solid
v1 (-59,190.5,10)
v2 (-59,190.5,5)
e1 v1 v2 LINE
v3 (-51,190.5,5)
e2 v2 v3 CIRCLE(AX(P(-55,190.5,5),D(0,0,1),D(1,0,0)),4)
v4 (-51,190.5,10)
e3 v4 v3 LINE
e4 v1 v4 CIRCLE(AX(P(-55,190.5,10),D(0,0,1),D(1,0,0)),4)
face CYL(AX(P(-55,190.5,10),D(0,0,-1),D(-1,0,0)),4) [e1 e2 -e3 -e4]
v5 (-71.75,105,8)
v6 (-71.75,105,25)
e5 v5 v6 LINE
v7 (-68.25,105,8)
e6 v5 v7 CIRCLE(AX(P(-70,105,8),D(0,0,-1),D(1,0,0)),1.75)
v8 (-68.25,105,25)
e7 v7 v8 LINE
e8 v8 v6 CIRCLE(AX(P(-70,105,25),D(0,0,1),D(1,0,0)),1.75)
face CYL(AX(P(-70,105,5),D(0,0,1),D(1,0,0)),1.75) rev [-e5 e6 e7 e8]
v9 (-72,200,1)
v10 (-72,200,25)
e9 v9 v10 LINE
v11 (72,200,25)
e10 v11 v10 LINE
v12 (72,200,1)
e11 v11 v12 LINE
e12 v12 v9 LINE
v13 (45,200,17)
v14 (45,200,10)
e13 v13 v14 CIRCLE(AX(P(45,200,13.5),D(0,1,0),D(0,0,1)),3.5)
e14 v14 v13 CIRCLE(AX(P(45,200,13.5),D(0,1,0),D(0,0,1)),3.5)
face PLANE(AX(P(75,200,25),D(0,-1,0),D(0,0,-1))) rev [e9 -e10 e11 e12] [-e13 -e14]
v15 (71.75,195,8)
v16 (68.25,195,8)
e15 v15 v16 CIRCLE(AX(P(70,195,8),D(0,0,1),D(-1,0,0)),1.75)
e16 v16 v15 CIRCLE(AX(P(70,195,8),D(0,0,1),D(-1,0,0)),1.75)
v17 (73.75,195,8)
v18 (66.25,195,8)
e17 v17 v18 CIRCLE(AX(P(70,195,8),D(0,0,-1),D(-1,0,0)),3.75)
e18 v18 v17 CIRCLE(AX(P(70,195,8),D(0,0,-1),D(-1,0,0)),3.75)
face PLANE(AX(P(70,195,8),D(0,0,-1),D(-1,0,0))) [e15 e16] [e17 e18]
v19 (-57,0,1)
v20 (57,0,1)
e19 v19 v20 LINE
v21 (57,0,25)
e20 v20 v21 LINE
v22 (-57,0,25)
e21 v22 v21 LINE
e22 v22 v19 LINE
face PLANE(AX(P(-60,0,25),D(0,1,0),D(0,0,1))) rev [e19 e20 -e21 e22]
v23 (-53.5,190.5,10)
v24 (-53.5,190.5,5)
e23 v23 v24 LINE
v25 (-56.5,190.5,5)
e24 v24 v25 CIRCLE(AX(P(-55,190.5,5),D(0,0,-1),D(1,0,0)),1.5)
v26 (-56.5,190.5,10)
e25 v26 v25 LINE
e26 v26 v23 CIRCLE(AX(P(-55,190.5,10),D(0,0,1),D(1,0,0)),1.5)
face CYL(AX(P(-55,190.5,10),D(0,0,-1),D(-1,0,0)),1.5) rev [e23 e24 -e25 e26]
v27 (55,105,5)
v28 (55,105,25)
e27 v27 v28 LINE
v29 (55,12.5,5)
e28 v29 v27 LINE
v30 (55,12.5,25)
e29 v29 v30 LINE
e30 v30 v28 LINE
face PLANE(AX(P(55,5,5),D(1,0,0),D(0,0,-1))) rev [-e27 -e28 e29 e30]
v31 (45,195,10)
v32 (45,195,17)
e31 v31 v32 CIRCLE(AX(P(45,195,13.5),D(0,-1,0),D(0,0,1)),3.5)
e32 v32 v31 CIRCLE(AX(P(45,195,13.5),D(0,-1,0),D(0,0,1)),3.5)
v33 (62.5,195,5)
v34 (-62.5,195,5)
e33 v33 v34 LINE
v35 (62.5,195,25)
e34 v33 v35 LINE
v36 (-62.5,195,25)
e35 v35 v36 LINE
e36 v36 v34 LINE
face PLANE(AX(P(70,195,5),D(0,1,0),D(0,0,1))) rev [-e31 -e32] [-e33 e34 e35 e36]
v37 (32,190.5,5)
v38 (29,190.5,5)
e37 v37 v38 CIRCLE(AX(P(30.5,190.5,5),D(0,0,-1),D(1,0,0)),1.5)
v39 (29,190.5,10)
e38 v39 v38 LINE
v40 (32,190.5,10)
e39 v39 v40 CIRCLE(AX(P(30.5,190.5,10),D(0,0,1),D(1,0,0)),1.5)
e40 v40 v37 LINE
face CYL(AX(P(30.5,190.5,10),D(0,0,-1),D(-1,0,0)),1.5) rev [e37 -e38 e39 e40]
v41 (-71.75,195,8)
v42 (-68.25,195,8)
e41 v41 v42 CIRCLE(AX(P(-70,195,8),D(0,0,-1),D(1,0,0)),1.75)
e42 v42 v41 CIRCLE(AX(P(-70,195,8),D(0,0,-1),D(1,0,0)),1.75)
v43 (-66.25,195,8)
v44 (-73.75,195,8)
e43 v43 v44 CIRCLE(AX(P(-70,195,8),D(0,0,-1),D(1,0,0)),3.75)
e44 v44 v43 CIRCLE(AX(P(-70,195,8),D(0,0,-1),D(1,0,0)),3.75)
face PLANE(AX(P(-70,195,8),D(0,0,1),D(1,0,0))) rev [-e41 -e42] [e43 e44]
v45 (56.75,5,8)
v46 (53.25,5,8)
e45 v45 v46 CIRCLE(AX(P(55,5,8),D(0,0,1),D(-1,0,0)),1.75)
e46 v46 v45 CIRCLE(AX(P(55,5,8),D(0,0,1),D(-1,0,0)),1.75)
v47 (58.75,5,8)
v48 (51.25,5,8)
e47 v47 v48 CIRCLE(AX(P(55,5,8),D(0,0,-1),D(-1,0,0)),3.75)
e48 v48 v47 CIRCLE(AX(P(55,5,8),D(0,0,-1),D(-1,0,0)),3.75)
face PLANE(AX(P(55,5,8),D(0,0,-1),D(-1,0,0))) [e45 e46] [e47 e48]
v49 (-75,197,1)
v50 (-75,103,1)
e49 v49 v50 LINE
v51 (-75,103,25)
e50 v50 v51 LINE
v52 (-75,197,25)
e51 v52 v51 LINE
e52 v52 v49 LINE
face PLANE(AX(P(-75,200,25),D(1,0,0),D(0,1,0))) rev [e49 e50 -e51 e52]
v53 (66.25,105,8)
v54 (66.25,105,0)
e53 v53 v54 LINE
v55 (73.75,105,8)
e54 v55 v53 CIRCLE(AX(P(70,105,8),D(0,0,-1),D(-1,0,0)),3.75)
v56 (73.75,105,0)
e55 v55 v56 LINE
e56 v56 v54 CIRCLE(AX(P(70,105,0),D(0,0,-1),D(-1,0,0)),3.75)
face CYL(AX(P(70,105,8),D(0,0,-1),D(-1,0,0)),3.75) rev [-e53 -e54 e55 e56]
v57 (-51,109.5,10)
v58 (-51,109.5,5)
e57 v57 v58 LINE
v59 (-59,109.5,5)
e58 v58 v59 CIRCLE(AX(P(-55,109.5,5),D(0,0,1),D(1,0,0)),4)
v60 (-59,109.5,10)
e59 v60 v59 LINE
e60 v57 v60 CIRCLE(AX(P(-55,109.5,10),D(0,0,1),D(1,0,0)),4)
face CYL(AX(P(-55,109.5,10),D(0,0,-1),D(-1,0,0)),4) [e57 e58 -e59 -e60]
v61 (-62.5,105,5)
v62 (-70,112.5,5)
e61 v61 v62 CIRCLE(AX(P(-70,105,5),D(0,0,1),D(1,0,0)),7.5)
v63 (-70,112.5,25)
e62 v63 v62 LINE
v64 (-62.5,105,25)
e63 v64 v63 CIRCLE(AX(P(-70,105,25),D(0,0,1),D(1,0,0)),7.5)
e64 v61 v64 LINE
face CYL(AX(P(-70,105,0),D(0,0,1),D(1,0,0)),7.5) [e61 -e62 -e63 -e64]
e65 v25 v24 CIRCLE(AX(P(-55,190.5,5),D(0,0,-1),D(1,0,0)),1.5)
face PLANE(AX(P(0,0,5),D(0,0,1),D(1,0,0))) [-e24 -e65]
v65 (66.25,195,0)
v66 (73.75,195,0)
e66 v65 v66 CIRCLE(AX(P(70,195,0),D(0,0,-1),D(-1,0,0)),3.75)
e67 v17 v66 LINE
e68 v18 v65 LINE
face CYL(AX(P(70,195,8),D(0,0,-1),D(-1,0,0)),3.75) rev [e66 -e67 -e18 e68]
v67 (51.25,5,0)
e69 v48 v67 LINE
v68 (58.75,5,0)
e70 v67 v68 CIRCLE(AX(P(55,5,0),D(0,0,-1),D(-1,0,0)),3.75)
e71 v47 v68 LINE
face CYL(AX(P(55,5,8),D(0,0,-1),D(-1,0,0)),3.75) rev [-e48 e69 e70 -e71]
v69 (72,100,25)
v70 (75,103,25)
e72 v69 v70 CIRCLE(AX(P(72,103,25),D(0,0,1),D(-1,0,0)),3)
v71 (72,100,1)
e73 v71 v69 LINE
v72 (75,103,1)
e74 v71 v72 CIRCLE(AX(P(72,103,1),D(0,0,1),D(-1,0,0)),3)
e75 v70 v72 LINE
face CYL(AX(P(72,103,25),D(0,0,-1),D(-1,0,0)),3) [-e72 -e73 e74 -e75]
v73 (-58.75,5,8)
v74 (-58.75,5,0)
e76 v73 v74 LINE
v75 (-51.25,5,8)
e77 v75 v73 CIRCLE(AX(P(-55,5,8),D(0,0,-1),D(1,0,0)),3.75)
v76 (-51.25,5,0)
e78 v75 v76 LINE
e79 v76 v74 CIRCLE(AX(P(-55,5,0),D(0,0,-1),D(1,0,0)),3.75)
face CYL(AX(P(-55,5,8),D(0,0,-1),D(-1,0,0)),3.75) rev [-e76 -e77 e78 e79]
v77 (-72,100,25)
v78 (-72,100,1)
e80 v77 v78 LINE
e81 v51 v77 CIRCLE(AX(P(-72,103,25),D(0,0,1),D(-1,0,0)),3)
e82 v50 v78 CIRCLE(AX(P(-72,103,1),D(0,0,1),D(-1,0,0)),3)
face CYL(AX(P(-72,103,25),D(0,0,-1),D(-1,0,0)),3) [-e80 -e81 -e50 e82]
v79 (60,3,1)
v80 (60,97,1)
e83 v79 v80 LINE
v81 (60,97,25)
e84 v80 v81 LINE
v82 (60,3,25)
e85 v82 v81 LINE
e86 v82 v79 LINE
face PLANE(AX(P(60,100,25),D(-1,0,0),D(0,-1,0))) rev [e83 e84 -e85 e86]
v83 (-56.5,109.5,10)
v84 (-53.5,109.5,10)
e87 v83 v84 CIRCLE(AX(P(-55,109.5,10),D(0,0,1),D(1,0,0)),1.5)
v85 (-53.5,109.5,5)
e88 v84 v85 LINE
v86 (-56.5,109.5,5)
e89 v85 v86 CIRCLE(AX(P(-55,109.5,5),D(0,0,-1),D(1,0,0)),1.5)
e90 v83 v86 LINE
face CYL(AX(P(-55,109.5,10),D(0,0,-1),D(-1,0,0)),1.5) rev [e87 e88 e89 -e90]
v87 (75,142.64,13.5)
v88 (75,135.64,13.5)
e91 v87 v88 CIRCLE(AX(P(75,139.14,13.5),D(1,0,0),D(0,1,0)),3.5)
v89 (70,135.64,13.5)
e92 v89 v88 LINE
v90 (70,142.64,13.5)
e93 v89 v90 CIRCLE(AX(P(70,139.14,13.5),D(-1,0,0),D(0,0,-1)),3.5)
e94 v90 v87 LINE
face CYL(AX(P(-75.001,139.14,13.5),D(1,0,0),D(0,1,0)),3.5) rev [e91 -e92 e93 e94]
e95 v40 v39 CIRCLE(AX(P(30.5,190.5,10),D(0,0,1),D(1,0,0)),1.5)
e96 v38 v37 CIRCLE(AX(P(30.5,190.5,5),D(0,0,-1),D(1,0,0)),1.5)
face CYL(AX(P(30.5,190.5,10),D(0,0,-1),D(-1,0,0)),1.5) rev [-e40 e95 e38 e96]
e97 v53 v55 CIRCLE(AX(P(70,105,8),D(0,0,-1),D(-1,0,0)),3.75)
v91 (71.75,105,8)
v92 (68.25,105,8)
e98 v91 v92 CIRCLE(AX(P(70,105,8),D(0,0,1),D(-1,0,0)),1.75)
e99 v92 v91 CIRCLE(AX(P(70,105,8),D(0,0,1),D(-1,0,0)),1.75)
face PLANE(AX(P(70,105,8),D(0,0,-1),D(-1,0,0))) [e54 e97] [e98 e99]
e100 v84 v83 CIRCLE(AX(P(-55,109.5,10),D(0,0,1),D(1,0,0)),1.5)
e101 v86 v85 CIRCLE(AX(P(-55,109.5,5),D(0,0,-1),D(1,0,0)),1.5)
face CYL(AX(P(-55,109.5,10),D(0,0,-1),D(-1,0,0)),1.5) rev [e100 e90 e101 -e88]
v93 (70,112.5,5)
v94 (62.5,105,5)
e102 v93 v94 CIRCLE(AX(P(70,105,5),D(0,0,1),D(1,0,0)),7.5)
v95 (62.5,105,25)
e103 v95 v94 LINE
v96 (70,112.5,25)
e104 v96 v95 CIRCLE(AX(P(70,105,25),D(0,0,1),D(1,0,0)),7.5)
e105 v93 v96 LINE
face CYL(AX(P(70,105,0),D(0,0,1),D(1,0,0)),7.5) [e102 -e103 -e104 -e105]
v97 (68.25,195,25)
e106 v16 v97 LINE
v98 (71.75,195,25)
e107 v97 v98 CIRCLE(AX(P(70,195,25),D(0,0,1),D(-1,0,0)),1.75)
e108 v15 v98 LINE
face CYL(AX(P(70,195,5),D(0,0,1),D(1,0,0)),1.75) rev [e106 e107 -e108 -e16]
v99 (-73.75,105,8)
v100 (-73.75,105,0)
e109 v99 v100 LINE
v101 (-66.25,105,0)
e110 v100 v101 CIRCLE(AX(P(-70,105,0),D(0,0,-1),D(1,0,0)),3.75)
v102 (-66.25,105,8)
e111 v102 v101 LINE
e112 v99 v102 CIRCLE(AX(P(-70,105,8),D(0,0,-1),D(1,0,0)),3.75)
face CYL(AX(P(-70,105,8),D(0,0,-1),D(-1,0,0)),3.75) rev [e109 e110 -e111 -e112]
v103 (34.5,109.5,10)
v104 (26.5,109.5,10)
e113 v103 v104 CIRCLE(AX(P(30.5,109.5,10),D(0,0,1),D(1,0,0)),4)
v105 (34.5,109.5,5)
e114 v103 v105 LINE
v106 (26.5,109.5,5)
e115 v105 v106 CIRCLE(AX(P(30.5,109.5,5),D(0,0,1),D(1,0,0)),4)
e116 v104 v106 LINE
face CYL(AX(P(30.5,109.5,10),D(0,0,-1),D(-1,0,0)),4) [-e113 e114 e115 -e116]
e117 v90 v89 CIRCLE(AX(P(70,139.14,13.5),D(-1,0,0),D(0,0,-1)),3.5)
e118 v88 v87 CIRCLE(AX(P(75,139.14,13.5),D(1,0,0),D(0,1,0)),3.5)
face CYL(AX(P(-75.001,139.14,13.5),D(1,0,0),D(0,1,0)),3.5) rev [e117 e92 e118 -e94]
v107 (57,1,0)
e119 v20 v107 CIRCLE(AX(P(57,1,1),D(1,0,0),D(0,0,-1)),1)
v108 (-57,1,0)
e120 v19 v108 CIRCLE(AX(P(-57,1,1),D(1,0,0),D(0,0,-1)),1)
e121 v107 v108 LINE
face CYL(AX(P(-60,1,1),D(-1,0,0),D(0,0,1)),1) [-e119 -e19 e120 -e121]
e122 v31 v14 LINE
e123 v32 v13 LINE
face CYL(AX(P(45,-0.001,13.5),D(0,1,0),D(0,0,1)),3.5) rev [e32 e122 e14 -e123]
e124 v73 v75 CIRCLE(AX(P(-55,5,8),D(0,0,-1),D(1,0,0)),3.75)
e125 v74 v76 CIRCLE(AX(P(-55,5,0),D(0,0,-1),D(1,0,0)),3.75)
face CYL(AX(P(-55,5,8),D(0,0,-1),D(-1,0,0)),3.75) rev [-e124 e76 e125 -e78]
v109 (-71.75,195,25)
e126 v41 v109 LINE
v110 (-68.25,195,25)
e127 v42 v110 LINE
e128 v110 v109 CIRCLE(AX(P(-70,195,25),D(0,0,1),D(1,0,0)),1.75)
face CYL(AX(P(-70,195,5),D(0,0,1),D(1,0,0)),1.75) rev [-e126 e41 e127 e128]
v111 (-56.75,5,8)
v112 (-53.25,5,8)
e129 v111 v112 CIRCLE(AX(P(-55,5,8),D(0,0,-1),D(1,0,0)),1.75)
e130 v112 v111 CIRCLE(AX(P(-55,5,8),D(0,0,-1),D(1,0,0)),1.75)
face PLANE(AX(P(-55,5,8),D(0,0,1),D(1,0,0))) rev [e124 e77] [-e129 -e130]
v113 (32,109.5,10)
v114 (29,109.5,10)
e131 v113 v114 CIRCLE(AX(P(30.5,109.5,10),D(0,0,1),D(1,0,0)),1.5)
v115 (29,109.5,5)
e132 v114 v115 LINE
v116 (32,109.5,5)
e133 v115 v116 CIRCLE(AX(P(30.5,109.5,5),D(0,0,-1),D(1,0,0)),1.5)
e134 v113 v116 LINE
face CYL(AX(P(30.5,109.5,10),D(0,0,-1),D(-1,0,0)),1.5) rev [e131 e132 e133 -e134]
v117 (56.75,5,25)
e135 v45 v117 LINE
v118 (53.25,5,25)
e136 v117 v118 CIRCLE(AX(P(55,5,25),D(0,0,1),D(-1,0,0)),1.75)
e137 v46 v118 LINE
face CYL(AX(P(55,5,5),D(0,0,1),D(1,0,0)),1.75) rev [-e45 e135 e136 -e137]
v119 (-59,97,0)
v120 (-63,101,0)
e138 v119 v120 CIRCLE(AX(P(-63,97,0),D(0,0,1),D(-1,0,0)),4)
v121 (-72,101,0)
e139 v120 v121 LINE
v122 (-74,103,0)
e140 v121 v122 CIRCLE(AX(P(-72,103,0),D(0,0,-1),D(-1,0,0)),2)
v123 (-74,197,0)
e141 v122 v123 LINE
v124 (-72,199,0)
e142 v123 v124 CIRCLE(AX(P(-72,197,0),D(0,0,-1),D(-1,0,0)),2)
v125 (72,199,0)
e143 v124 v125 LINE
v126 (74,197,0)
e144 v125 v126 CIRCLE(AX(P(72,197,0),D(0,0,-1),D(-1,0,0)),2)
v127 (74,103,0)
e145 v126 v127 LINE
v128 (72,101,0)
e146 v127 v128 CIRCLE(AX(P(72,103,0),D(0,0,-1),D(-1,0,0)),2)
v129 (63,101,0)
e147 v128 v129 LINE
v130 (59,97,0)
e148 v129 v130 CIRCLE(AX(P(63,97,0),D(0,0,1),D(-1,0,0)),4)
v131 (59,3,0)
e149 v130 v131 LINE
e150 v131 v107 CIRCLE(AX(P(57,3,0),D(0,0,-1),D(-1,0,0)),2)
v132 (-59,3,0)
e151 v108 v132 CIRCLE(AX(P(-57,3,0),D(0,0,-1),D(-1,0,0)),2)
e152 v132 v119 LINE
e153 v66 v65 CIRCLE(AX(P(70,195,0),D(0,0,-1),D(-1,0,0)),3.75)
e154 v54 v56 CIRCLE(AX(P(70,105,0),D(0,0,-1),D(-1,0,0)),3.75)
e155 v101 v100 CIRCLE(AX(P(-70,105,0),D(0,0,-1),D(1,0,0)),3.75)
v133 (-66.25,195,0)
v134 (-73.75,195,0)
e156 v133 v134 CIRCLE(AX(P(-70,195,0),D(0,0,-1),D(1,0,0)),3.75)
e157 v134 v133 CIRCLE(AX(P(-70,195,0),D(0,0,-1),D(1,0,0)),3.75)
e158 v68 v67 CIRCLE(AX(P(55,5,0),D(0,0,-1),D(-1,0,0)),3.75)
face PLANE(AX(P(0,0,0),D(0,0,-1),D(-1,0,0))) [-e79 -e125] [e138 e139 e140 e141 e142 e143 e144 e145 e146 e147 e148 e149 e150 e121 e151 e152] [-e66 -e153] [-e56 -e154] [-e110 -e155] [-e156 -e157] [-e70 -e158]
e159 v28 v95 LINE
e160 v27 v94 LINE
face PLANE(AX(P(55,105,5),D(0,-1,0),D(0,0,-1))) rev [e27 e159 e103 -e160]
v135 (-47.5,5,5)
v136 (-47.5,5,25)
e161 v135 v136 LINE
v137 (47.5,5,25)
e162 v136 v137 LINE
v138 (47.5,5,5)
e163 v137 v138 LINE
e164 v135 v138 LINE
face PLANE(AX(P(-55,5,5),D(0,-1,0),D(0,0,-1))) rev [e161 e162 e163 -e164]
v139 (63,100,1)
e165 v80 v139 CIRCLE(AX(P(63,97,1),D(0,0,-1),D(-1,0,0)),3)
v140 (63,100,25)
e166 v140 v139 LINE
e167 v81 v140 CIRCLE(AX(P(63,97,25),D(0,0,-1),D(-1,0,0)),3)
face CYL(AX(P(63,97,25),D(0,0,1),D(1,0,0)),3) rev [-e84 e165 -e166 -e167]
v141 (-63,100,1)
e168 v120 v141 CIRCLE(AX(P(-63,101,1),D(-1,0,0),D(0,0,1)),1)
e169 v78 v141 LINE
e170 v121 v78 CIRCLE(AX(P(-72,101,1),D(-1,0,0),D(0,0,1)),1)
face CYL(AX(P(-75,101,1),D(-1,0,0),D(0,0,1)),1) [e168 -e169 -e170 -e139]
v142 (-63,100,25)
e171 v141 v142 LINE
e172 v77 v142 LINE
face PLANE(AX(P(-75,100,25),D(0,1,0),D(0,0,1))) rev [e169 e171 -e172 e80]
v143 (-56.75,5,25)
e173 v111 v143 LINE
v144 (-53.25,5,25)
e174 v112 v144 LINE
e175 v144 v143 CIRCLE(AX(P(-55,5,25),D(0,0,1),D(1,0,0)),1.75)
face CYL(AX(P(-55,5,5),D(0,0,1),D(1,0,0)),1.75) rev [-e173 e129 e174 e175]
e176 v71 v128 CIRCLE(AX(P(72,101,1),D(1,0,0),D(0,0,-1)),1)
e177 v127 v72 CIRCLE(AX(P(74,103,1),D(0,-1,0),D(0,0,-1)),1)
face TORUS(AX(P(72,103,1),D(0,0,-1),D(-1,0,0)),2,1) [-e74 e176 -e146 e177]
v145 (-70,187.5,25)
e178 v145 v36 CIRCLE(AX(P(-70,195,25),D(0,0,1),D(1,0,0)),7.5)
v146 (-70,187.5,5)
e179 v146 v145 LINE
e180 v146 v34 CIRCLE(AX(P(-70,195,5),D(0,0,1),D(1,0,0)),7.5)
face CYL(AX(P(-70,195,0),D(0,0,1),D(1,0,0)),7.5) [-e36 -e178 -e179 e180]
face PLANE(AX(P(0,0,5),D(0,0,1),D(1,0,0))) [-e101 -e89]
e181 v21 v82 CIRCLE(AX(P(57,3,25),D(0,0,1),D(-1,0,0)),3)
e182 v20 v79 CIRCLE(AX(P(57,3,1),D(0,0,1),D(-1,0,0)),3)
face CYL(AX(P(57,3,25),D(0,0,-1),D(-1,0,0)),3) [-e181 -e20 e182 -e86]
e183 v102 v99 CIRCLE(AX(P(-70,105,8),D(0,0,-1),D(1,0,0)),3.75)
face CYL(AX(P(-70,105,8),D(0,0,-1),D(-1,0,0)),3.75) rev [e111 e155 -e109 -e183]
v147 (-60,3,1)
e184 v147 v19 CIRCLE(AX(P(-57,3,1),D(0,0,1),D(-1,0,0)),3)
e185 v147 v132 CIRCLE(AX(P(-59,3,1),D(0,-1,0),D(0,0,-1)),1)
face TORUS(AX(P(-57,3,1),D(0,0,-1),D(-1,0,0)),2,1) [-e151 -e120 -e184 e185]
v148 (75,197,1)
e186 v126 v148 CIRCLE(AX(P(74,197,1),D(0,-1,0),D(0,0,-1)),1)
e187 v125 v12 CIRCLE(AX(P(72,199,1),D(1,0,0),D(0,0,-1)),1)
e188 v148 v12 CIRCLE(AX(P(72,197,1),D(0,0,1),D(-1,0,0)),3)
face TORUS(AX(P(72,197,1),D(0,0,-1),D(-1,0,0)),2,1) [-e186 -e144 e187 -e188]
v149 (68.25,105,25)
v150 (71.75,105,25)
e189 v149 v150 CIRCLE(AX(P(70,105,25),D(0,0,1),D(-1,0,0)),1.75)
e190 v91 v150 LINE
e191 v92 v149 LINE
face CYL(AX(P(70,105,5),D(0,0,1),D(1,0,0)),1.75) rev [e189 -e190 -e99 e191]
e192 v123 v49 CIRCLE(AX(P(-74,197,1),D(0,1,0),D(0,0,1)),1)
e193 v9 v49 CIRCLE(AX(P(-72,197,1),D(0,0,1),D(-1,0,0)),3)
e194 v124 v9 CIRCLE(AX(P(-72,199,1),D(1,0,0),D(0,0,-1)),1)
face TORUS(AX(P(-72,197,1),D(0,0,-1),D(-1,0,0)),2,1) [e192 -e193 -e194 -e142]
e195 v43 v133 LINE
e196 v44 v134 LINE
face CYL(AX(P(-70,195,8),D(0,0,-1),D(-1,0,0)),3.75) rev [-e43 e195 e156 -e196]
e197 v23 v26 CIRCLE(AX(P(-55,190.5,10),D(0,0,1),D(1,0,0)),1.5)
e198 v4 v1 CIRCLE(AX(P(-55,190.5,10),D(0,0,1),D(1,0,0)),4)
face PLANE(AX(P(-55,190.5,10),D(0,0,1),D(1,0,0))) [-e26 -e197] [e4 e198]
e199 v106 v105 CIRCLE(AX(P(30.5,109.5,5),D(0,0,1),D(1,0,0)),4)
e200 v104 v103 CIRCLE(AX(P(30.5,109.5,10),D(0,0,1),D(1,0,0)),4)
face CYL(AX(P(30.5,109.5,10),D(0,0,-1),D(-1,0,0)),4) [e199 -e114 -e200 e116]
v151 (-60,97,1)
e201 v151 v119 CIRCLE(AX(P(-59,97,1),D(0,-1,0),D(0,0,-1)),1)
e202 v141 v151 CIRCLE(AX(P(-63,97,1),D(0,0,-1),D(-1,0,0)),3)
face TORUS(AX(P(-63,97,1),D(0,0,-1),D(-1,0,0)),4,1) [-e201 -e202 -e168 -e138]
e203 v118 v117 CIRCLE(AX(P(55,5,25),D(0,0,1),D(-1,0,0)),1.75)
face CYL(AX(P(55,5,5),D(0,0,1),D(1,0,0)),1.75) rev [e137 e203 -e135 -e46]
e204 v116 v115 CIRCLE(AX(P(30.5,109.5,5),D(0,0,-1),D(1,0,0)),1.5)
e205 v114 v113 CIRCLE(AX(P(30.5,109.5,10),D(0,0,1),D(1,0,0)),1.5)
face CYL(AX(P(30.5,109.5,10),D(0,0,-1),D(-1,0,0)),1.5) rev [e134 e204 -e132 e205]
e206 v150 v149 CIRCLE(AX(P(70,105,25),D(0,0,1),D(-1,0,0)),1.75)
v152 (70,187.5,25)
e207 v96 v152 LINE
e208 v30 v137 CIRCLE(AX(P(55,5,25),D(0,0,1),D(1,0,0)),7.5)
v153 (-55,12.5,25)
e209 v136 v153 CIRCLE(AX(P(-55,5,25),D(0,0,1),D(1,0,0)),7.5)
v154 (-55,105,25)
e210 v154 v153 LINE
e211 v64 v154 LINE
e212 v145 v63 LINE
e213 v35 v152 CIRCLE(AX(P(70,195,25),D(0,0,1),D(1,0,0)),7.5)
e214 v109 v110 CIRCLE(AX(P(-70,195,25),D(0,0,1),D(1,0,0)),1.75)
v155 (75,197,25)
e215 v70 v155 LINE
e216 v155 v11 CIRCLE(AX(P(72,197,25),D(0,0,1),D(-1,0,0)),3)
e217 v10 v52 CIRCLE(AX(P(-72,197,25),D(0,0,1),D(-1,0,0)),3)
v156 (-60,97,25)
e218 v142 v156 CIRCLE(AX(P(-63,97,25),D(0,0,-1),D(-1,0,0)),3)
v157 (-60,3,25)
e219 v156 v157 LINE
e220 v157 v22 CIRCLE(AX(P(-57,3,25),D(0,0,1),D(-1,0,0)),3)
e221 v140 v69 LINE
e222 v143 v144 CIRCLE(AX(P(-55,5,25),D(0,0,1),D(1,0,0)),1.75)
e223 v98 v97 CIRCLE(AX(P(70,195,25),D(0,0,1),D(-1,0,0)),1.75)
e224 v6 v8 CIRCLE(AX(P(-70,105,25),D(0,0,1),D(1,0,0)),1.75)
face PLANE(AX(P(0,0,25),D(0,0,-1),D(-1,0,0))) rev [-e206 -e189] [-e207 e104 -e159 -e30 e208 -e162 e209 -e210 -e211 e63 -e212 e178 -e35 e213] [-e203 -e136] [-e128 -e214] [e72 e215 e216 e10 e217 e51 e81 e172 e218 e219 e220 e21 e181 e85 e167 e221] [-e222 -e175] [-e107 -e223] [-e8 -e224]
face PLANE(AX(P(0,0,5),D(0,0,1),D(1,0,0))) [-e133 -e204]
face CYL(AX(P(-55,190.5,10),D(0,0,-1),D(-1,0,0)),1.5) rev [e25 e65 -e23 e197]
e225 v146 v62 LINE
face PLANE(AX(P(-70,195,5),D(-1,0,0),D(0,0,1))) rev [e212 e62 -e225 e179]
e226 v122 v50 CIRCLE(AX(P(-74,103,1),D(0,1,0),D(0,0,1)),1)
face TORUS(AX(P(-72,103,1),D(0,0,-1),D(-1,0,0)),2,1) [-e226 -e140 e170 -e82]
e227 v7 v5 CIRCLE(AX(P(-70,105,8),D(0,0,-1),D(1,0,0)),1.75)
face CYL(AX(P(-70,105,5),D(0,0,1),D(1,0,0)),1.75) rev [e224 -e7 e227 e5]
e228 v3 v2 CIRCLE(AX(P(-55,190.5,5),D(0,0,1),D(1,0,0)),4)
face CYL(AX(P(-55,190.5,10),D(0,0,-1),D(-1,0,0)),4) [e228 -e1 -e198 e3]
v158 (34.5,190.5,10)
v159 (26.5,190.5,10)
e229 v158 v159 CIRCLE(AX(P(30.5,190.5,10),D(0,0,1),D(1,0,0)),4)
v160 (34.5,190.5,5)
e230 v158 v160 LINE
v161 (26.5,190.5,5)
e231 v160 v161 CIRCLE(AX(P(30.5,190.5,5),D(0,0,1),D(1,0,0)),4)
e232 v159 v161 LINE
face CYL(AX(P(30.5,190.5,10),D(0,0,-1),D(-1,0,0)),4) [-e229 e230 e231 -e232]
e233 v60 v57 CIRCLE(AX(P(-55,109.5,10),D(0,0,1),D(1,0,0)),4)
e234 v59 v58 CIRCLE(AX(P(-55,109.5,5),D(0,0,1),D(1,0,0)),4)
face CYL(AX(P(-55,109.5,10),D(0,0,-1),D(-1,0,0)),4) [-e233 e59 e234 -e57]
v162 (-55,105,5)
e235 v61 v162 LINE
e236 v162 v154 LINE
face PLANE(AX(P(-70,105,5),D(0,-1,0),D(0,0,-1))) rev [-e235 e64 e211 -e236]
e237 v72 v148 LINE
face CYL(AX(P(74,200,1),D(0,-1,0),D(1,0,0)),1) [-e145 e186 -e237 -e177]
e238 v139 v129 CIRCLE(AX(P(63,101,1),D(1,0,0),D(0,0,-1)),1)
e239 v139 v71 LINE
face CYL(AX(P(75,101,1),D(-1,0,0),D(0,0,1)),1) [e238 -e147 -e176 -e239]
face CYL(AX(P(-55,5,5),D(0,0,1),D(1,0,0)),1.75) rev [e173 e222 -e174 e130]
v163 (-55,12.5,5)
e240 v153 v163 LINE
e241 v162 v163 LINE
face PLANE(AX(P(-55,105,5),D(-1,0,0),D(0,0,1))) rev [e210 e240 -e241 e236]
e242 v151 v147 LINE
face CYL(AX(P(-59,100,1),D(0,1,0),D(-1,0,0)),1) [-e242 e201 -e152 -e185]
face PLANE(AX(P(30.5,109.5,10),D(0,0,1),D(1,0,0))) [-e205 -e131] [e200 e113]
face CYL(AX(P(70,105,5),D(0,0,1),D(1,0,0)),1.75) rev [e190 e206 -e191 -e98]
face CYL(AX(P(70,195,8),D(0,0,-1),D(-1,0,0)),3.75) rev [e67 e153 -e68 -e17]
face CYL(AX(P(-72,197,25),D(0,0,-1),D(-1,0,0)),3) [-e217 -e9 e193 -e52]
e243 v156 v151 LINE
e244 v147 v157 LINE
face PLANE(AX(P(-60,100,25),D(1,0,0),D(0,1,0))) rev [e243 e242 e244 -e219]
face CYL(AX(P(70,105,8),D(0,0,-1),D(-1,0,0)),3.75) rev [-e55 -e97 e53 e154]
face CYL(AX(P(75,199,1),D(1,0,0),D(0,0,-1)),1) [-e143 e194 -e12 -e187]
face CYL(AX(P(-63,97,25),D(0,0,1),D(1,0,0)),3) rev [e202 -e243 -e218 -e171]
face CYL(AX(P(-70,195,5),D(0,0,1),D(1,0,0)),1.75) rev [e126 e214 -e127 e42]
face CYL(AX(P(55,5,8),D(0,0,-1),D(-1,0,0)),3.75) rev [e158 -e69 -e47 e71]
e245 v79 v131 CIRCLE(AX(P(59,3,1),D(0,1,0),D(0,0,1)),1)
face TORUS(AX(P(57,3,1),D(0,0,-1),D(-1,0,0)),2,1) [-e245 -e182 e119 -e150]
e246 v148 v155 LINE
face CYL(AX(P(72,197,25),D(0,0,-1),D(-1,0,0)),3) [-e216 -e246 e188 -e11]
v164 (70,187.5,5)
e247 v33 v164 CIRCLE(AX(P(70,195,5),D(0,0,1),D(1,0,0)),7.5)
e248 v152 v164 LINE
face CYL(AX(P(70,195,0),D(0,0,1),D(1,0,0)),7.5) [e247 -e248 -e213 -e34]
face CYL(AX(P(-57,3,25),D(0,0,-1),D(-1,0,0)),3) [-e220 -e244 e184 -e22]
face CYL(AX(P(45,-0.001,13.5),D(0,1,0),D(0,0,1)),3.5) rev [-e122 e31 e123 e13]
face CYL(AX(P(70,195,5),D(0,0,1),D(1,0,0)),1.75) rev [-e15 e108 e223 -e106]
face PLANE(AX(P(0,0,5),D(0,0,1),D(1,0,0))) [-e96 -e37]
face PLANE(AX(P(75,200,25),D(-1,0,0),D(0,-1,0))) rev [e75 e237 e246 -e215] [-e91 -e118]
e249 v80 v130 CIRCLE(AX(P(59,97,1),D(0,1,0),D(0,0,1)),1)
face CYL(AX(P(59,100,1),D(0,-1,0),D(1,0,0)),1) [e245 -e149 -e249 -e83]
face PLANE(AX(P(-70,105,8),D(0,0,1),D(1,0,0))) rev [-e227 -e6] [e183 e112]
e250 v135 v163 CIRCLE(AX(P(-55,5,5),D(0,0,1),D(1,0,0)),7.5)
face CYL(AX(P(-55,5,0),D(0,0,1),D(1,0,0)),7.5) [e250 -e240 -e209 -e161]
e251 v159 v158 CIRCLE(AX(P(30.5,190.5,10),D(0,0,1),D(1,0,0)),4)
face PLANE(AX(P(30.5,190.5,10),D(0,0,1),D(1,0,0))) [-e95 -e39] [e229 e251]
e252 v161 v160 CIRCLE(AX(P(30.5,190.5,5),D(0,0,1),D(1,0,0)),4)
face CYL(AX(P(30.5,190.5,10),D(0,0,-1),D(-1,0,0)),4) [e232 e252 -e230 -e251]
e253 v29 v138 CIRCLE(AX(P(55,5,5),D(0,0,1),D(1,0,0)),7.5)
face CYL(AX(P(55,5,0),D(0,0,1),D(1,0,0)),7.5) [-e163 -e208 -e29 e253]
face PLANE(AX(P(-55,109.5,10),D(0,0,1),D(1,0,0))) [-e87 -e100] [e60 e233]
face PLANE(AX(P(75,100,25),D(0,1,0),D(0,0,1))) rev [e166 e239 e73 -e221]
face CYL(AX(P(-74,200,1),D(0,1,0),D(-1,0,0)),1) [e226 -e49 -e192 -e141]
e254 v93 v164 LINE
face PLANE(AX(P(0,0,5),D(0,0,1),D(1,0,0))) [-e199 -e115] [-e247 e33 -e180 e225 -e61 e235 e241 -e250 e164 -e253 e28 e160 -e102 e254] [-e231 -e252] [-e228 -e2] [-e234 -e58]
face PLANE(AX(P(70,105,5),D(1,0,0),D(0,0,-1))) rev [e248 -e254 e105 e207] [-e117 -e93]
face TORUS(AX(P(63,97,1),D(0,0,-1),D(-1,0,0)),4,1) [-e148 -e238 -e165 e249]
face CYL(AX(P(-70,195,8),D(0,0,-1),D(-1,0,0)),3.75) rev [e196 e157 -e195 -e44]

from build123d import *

# Parameters (mm, degrees)
BOSS_EXTRUDE1_DEPTH = 25
CUT_EXTRUDE1_DEPTH  = 20
FILLET1_R           = 3
FILLET2_R           = 1
SKETCH5_R           = 4
SKETCH5_R_2         = 1.5
BOSS_EXTRUDE2_DEPTH = 5
BOSS_EXTRUDE3_DEPTH = 25
SKETCH7_R           = 1.75
CUT_EXTRUDE4_DEPTH  = 20
SKETCH8_R           = 3.75
CUT_EXTRUDE5_DEPTH  = 8
CUT_EXTRUDE6_REACH  = 253.247
SKETCH9_R           = 3.5
CUT_EXTRUDE7_REACH  = 217.058
SKETCH10_R          = 3.5


with BuildPart() as part:
    # Sketch1 → Boss-Extrude1 (new body)
    with BuildSketch(Plane.XY):
        Polygon((75, 200), (-75, 200), (-75, 100), (-60, 100), (-60, 0), (60, 0), (60, 100), (75, 100), align=None)
    extrude(amount=BOSS_EXTRUDE1_DEPTH)

    # Sketch2 → Cut-Extrude1 (cut)
    with BuildSketch(Plane.XY.offset(25)):
        Polygon((70, 105), (70, 195), (-70, 195), (-70, 105), (-55, 105), (-55, 5), (55, 5), (55, 105), align=None)
    extrude(amount=-CUT_EXTRUDE1_DEPTH, mode=Mode.SUBTRACT)

    # Fillet1
    fillet1_edges = [part.edges().sort_by_distance(p)[0] for p in [
        (-75, 100, 12.5),
        (-75, 200, 12.5),
        (75, 200, 12.5),
        (75, 100, 12.5),
        (60, 100, 12.5),
        (60, 0, 12.5),
        (-60, 0, 12.5),
        (-60, 100, 12.5),
    ]]
    fillet(fillet1_edges, radius=FILLET1_R)

    # Fillet2
    fillet2_edges = [part.edges().sort_by_distance(p)[0] for p in [
        (67.5, 100, 0),
        (60, 50, 0),
        (-60, 50, 0),
        (-67.5, 100, 0),
        (0, 0, 0),
        (-75, 150, 0),
        (0, 200, 0),
        (75, 150, 0),
        (-74.121320344, 199.121320344, 0),
        (-74.121320344, 100.878679656, 0),
        (74.121320344, 199.121320344, 0),
        (74.121320344, 100.878679656, 0),
        (59.121320344, 0.878679656, 0),
        (-59.121320344, 0.878679656, 0),
        (60.878679656, 99.121320344, 0),
        (-60.878679656, 99.121320344, 0),
    ]]
    fillet(fillet2_edges, radius=FILLET2_R)

    # Sketch5 → Boss-Extrude2 (add)
    # profile 1 of 4: a face of its own
    with BuildSketch(Plane.XY.offset(5)):
        with Locations((-55, 190.5)):
            Circle(SKETCH5_R)
        with Locations((-55, 190.5)):
            Circle(SKETCH5_R_2, mode=Mode.SUBTRACT)
    # profile 2 of 4: a face of its own
    with BuildSketch(Plane.XY.offset(5)):
        with Locations((30.5, 190.5)):
            Circle(SKETCH5_R)
        with Locations((30.5, 190.5)):
            Circle(SKETCH5_R_2, mode=Mode.SUBTRACT)
    # profile 3 of 4: a face of its own
    with BuildSketch(Plane.XY.offset(5)):
        with Locations((-55, 109.5)):
            Circle(SKETCH5_R)
        with Locations((-55, 109.5)):
            Circle(SKETCH5_R_2, mode=Mode.SUBTRACT)
    # profile 4 of 4: a face of its own
    with BuildSketch(Plane.XY.offset(5)):
        with Locations((30.5, 109.5)):
            Circle(SKETCH5_R)
        with Locations((30.5, 109.5)):
            Circle(SKETCH5_R_2, mode=Mode.SUBTRACT)
    extrude(amount=BOSS_EXTRUDE2_DEPTH)

    # Sketch6 → Boss-Extrude3 (add)
    with BuildSketch(Plane.XY.offset(25)):
        with BuildLine():
            Line((-71.747064875, 196.748861378), (-62.706750801, 196.748861378))
            ThreePointArc((-62.706750801, 196.748861378), (-64.696046035, 189.697352328), (-71.747064875, 187.706320248))
            Line((-71.747064875, 187.706320248), (-71.747064875, 196.748861378))
        make_face()
        with BuildLine():
            Line((71.50031539, 195.771596957), (62.539796374, 195.771596957))
            ThreePointArc((62.539796374, 195.771596957), (64.963763881, 189.442453262), (71.50031539, 187.651595157))
            Line((71.50031539, 187.651595157), (71.50031539, 195.771596957))
        make_face()
        with BuildLine():
            Line((71.50031539, 103.139966112), (62.734308434, 103.139966112))
            ThreePointArc((62.734308434, 103.139966112), (64.567806467, 110.171196518), (71.50031539, 112.348404843))
            Line((71.50031539, 112.348404843), (71.50031539, 103.139966112))
        make_face()
        with BuildLine():
            Line((-56.424780788, 4.339960717), (-47.529099911, 4.339960717))
            ThreePointArc((-47.529099911, 4.339960717), (-49.976766301, 10.56930186), (-56.424780788, 12.363423097))
            Line((-56.424780788, 12.363423097), (-56.424780788, 4.339960717))
        make_face()
        with BuildLine():
            Line((56.315887188, 4.339960717), (47.529099911, 4.339960717))
            ThreePointArc((47.529099911, 4.339960717), (49.935780208, 10.532059101), (56.315887188, 12.3836604))
            Line((56.315887188, 12.3836604), (56.315887188, 4.339960717))
        make_face()
        with BuildLine():
            Line((-71.747064875, 102.631768342), (-62.883717346, 102.631768342))
            ThreePointArc((-62.883717346, 102.631768342), (-64.473223551, 110.069984427), (-71.747064875, 112.293679752))
            Line((-71.747064875, 112.293679752), (-71.747064875, 102.631768342))
        make_face()
    extrude(amount=-BOSS_EXTRUDE3_DEPTH)

    # Sketch7 → Cut-Extrude4 (cut)
    with BuildSketch(Plane.XY.offset(25)):
        with Locations((-70, 195)):
            Circle(SKETCH7_R)
        with Locations((-70, 105)):
            Circle(SKETCH7_R)
        with Locations((-55, 5)):
            Circle(SKETCH7_R)
        with Locations(Location((55, 5, 0), (0, 0, 180))):
            Circle(SKETCH7_R)
        with Locations(Location((70, 105, 0), (0, 0, 180))):
            Circle(SKETCH7_R)
        with Locations(Location((70, 195, 0), (0, 0, 180))):
            Circle(SKETCH7_R)
    extrude(amount=-CUT_EXTRUDE4_DEPTH, mode=Mode.SUBTRACT)

    # Sketch8 → Cut-Extrude5 (cut)
    with BuildSketch(Plane(origin=(0, 0, 0), x_dir=(-1, 0, 0), z_dir=(0, 0, -1))):
        with Locations((-70, 195)):
            Circle(SKETCH8_R)
        with Locations((-70, 105)):
            Circle(SKETCH8_R)
        with Locations((-55, 5)):
            Circle(SKETCH8_R)
        with Locations(Location((55, 5, 0), (0, 0, 180))):
            Circle(SKETCH8_R)
        with Locations(Location((70, 105, 0), (0, 0, 180))):
            Circle(SKETCH8_R)
        with Locations(Location((70, 195, 0), (0, 0, 180))):
            Circle(SKETCH8_R)
    extrude(amount=-CUT_EXTRUDE5_DEPTH, mode=Mode.SUBTRACT)

    # Sketch9 → Cut-Extrude6 (cut, up to next)
    with BuildSketch(Plane(origin=(75, 0, 0), x_dir=(0, 0, -1), z_dir=(1, 0, 0)), mode=Mode.PRIVATE) as cut_extrude6_sk1:
        with Locations(Location((-13.5, 139.14, 0), (0, 0, 90))):
            Circle(SKETCH9_R)
    cut_extrude6_tool1 = extrude(cut_extrude6_sk1.sketch, amount=-CUT_EXTRUDE6_REACH, mode=Mode.PRIVATE) & part.part
    add(cut_extrude6_tool1.solids().sort_by_distance((75, 139.14, 13.5))[0], mode=Mode.SUBTRACT)

    # Sketch10 → Cut-Extrude7 (cut, up to next)
    with BuildSketch(Plane(origin=(0, 200, 0), x_dir=(1, 0, 0), z_dir=(0, 1, 0)), mode=Mode.PRIVATE) as cut_extrude7_sk1:
        with Locations(Location((45, -13.5, 0), (0, 0, 270))):
            Circle(SKETCH10_R)
    cut_extrude7_tool1 = extrude(cut_extrude7_sk1.sketch, amount=-CUT_EXTRUDE7_REACH, mode=Mode.PRIVATE) & part.part
    add(cut_extrude7_tool1.solids().sort_by_distance((45, 200, 13.5))[0], mode=Mode.SUBTRACT)


solid = part.part
